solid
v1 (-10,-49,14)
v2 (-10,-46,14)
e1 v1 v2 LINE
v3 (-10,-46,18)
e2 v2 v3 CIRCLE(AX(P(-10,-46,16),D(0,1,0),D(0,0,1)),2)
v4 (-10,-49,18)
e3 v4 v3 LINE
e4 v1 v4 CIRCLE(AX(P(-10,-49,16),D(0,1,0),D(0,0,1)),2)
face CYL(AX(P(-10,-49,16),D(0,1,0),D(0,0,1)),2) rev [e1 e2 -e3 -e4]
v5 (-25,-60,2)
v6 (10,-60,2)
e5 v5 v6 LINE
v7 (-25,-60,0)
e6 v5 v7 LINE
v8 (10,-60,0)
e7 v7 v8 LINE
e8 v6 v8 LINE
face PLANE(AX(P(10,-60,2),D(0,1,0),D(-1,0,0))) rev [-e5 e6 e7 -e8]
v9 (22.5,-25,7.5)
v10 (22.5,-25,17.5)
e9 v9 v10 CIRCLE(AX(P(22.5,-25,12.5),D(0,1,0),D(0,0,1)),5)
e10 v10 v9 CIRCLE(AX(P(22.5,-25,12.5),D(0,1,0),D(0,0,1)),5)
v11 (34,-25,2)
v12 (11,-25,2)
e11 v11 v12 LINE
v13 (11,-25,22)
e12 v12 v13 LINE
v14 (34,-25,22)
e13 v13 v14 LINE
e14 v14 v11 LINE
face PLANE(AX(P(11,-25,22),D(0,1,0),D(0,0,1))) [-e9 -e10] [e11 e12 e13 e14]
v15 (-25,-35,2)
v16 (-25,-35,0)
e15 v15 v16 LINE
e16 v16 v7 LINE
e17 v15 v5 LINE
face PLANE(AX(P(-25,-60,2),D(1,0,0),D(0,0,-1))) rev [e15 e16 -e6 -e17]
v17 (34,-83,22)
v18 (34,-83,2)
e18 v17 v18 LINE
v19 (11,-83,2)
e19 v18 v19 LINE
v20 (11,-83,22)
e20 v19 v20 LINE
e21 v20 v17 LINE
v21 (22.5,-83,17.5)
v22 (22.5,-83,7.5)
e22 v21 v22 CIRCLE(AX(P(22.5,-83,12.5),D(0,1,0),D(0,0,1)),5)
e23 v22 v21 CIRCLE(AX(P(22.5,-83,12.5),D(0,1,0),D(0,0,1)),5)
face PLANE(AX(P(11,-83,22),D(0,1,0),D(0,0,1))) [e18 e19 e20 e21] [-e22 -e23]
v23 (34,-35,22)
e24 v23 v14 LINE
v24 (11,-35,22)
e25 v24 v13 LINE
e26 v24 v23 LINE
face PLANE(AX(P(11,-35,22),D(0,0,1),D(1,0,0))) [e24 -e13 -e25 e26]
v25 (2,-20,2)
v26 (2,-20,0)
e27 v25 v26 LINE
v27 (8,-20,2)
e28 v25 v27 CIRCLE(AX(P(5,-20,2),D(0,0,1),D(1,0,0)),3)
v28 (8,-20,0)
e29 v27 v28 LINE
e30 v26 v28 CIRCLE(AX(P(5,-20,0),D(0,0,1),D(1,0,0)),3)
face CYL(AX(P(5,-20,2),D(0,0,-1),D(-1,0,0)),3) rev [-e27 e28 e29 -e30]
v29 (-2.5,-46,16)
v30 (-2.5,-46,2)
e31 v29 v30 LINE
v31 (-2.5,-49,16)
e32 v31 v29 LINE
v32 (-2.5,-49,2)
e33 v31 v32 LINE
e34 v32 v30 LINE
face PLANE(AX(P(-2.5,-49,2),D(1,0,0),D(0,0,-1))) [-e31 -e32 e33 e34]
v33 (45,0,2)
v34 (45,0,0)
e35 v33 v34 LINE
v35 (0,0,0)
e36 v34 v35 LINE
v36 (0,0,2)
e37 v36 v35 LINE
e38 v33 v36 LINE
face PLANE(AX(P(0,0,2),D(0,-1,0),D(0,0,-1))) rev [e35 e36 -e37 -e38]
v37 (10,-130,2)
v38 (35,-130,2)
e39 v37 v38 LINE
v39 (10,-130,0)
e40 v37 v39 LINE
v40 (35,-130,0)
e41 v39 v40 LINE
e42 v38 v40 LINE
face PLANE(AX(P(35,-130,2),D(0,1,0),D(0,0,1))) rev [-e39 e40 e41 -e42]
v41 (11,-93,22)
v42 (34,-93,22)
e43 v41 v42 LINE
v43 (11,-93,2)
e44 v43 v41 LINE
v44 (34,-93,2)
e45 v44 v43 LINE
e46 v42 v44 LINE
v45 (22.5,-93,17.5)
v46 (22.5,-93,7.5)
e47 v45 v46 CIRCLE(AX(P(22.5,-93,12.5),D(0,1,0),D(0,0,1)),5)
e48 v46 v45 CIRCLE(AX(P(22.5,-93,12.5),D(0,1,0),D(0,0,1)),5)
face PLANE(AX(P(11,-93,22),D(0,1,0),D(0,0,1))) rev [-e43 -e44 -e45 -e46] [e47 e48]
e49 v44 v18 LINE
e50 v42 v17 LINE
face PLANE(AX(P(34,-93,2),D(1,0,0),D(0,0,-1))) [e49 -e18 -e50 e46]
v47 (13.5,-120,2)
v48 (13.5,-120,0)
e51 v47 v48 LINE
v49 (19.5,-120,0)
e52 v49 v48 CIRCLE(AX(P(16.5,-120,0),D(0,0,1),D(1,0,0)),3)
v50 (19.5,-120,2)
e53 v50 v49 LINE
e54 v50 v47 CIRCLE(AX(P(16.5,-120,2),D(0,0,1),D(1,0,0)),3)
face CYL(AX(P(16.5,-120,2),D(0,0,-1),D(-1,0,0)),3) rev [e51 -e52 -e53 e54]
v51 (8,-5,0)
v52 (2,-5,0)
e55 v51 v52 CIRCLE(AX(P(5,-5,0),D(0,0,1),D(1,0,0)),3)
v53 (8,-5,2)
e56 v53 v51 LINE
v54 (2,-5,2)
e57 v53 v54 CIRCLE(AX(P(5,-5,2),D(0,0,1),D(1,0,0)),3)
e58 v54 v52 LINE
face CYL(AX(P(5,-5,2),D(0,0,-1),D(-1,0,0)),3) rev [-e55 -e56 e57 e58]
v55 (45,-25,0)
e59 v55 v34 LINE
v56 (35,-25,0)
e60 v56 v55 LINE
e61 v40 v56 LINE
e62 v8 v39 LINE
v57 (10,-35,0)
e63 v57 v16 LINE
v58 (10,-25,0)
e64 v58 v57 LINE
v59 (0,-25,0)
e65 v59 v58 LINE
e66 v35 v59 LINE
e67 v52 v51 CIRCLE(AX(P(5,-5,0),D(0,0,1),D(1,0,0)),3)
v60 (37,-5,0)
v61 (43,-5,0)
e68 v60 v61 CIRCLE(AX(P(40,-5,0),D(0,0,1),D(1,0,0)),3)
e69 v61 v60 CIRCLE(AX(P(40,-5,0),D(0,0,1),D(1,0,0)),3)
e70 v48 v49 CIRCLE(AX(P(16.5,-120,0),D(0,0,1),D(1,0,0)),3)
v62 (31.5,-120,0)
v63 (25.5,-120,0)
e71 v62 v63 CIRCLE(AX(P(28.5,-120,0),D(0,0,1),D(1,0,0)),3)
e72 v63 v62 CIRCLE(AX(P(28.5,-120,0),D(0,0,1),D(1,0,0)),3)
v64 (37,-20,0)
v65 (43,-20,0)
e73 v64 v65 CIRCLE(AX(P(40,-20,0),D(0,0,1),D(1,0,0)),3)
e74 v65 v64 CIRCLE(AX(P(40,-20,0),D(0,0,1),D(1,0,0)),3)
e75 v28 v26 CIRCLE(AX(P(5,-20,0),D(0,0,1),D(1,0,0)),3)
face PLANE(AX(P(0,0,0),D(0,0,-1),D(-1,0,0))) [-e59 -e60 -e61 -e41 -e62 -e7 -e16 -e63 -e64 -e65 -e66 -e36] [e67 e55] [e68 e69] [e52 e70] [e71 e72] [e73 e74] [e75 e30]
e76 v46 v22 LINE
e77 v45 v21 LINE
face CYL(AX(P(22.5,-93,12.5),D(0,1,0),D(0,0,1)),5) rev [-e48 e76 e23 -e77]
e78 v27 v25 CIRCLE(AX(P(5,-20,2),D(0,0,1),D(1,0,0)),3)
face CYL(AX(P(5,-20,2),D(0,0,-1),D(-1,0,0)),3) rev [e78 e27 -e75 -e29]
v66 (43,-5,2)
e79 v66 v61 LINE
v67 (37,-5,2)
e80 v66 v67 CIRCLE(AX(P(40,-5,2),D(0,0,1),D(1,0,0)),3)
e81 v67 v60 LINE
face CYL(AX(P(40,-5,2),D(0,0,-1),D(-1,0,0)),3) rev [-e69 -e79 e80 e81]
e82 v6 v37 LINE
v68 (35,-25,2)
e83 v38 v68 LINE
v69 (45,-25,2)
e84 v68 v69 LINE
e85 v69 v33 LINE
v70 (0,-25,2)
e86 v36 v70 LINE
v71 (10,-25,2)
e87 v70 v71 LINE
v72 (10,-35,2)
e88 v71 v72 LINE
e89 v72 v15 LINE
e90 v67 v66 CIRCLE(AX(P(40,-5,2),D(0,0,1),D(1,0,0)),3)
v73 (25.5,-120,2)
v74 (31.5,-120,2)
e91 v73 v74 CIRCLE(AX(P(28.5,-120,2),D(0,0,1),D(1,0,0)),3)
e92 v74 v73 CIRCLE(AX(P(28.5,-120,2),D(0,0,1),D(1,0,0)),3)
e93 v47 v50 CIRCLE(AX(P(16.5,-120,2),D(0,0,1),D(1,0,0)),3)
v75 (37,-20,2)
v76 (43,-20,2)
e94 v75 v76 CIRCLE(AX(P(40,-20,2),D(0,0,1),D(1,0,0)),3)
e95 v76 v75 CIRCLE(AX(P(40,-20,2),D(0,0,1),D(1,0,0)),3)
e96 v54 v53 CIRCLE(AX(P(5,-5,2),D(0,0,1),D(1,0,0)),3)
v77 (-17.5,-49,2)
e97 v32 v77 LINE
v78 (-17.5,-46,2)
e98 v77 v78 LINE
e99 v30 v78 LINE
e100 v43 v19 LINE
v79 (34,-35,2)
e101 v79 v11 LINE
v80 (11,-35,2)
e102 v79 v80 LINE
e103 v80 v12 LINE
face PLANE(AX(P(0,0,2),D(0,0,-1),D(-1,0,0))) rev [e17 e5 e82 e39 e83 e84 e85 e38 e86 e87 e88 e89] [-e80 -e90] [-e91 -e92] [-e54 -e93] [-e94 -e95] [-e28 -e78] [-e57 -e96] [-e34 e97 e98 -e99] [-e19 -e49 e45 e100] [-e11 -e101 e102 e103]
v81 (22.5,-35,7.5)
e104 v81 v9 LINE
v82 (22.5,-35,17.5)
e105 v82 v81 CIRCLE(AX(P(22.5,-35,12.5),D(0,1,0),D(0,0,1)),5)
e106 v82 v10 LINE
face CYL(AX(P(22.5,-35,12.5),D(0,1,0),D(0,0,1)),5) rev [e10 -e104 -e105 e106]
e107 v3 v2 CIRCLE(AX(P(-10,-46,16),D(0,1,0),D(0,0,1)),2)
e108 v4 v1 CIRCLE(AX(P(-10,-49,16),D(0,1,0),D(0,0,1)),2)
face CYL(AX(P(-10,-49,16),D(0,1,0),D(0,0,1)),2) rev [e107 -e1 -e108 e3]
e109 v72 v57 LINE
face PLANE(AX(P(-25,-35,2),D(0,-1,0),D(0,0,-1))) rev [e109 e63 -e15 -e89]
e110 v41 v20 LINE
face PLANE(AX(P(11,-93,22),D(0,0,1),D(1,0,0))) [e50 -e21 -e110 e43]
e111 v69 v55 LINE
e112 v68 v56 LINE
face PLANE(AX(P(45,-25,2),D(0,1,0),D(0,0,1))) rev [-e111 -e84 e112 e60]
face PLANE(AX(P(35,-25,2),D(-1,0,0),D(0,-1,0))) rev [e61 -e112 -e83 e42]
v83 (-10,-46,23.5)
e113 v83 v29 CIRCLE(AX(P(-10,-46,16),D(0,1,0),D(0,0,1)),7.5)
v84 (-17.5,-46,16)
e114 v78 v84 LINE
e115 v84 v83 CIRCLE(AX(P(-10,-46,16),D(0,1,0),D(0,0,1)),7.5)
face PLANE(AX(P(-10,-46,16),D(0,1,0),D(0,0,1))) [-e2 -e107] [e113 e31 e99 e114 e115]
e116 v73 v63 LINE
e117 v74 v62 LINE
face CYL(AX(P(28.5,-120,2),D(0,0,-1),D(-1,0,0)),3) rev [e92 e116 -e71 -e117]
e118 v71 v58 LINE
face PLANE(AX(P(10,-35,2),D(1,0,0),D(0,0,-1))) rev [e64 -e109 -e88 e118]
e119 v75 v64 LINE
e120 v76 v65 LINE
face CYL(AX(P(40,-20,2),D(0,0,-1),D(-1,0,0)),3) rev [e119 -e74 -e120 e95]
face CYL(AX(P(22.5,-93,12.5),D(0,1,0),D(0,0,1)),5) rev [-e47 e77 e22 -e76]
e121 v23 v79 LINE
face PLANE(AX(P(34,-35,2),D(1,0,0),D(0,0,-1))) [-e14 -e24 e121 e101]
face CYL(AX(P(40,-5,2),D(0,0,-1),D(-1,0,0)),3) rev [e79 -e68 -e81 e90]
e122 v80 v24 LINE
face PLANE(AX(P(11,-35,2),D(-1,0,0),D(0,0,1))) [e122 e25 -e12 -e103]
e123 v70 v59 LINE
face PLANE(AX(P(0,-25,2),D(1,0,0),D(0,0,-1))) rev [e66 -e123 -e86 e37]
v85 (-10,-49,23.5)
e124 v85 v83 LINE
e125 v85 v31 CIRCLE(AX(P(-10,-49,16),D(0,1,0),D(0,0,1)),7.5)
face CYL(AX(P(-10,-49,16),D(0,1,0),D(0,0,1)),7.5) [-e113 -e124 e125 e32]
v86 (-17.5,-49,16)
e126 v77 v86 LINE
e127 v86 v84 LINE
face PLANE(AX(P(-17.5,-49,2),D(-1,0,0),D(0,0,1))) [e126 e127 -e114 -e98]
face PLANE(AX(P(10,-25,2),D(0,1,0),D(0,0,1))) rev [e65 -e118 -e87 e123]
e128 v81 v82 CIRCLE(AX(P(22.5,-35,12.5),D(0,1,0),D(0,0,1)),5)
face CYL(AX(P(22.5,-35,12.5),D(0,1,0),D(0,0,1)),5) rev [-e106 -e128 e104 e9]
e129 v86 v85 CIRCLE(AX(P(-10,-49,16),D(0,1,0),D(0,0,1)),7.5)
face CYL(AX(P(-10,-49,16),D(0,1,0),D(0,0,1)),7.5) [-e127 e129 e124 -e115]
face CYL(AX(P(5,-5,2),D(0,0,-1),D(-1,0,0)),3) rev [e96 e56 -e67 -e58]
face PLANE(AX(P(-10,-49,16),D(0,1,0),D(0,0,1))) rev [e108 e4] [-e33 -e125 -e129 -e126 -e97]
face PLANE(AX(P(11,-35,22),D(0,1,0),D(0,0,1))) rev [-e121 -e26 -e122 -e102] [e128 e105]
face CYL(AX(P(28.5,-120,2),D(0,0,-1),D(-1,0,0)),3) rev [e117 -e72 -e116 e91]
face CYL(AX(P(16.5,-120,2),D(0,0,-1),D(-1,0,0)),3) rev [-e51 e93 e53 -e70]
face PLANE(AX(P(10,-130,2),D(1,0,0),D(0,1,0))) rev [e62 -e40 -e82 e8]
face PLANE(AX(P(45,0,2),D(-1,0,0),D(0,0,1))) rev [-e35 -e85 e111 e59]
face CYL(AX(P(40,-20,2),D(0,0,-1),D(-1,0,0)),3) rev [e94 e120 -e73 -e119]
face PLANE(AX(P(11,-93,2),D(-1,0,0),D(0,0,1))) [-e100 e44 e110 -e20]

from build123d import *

# Parameters (mm, degrees)
SKETCH_1_R             = 3
EXTRUDE_1_DEPTH        = 2
EXTRUDE_START          = -25
SKETCH_2_W             = 23
SKETCH_2_H             = 20
SKETCH_2_R             = 5
EXTRUDE_2_DEPTH        = 10
PATTERN_LINEAR_1_COUNT = 2
PATTERN_LINEAR_1_PITCH = 58
EXTRUDE_START_2        = -11
SKETCH_3_R             = 2
EXTRUDE_3_DEPTH        = 3


with BuildPart() as part:
    # 草图1 → 凸台-拉伸1 (new body)
    with BuildSketch(Plane.XY):
        Polygon((0, 0), (45, 0), (45, -25), (35, -25), (35, -130), (10, -130), (10, -60), (-25, -60), (-25, -35), (10, -35), (10, -25), (0, -25), align=None)
        with Locations((5, -5)):
            Circle(SKETCH_1_R, mode=Mode.SUBTRACT)
        with Locations((40, -5)):
            Circle(SKETCH_1_R, mode=Mode.SUBTRACT)
        with Locations((5, -20)):
            Circle(SKETCH_1_R, mode=Mode.SUBTRACT)
        with Locations((40, -20)):
            Circle(SKETCH_1_R, mode=Mode.SUBTRACT)
        with Locations((16.5, -120)):
            Circle(SKETCH_1_R, mode=Mode.SUBTRACT)
        with Locations((28.5, -120)):
            Circle(SKETCH_1_R, mode=Mode.SUBTRACT)
    extrude(amount=EXTRUDE_1_DEPTH)

    # 草图2 → 凸台-拉伸2 (add)
    with BuildSketch(Plane(origin=(0, 0, 0), x_dir=(1, 0, 0), z_dir=(0, 1, 0)).offset(EXTRUDE_START)):
        with Locations((22.5, -12)):
            Rectangle(SKETCH_2_W, SKETCH_2_H)
        with Locations(Location((22.5, -12.5, 0), (0, 0, 270))):
            Circle(SKETCH_2_R, mode=Mode.SUBTRACT)
    extrude_2 = extrude(amount=-EXTRUDE_2_DEPTH)

    # 阵列(线性)1: 凸台-拉伸2 ×2
    with Locations(*[(0, -i * PATTERN_LINEAR_1_PITCH, 0) for i in range(1, PATTERN_LINEAR_1_COUNT)]):
        add(extrude_2)

    # 草图3 → 凸台-拉伸3 (add)
    with BuildSketch(Plane(origin=(0, -35, 0), x_dir=(1, 0, 0), z_dir=(0, 1, 0)).offset(EXTRUDE_START_2)):
        with BuildLine():
            Line((-17.5, -2), (-2.5, -2))
            Line((-2.5, -2), (-2.5, -16))
            ThreePointArc((-2.5, -16), (-10, -23.5), (-17.5, -16))
            Line((-17.5, -16), (-17.5, -2))
        make_face()
        with Locations(Location((-10, -16, 0), (0, 0, 270))):
            Circle(SKETCH_3_R, mode=Mode.SUBTRACT)
    extrude(amount=-EXTRUDE_3_DEPTH)


solid = part.part
